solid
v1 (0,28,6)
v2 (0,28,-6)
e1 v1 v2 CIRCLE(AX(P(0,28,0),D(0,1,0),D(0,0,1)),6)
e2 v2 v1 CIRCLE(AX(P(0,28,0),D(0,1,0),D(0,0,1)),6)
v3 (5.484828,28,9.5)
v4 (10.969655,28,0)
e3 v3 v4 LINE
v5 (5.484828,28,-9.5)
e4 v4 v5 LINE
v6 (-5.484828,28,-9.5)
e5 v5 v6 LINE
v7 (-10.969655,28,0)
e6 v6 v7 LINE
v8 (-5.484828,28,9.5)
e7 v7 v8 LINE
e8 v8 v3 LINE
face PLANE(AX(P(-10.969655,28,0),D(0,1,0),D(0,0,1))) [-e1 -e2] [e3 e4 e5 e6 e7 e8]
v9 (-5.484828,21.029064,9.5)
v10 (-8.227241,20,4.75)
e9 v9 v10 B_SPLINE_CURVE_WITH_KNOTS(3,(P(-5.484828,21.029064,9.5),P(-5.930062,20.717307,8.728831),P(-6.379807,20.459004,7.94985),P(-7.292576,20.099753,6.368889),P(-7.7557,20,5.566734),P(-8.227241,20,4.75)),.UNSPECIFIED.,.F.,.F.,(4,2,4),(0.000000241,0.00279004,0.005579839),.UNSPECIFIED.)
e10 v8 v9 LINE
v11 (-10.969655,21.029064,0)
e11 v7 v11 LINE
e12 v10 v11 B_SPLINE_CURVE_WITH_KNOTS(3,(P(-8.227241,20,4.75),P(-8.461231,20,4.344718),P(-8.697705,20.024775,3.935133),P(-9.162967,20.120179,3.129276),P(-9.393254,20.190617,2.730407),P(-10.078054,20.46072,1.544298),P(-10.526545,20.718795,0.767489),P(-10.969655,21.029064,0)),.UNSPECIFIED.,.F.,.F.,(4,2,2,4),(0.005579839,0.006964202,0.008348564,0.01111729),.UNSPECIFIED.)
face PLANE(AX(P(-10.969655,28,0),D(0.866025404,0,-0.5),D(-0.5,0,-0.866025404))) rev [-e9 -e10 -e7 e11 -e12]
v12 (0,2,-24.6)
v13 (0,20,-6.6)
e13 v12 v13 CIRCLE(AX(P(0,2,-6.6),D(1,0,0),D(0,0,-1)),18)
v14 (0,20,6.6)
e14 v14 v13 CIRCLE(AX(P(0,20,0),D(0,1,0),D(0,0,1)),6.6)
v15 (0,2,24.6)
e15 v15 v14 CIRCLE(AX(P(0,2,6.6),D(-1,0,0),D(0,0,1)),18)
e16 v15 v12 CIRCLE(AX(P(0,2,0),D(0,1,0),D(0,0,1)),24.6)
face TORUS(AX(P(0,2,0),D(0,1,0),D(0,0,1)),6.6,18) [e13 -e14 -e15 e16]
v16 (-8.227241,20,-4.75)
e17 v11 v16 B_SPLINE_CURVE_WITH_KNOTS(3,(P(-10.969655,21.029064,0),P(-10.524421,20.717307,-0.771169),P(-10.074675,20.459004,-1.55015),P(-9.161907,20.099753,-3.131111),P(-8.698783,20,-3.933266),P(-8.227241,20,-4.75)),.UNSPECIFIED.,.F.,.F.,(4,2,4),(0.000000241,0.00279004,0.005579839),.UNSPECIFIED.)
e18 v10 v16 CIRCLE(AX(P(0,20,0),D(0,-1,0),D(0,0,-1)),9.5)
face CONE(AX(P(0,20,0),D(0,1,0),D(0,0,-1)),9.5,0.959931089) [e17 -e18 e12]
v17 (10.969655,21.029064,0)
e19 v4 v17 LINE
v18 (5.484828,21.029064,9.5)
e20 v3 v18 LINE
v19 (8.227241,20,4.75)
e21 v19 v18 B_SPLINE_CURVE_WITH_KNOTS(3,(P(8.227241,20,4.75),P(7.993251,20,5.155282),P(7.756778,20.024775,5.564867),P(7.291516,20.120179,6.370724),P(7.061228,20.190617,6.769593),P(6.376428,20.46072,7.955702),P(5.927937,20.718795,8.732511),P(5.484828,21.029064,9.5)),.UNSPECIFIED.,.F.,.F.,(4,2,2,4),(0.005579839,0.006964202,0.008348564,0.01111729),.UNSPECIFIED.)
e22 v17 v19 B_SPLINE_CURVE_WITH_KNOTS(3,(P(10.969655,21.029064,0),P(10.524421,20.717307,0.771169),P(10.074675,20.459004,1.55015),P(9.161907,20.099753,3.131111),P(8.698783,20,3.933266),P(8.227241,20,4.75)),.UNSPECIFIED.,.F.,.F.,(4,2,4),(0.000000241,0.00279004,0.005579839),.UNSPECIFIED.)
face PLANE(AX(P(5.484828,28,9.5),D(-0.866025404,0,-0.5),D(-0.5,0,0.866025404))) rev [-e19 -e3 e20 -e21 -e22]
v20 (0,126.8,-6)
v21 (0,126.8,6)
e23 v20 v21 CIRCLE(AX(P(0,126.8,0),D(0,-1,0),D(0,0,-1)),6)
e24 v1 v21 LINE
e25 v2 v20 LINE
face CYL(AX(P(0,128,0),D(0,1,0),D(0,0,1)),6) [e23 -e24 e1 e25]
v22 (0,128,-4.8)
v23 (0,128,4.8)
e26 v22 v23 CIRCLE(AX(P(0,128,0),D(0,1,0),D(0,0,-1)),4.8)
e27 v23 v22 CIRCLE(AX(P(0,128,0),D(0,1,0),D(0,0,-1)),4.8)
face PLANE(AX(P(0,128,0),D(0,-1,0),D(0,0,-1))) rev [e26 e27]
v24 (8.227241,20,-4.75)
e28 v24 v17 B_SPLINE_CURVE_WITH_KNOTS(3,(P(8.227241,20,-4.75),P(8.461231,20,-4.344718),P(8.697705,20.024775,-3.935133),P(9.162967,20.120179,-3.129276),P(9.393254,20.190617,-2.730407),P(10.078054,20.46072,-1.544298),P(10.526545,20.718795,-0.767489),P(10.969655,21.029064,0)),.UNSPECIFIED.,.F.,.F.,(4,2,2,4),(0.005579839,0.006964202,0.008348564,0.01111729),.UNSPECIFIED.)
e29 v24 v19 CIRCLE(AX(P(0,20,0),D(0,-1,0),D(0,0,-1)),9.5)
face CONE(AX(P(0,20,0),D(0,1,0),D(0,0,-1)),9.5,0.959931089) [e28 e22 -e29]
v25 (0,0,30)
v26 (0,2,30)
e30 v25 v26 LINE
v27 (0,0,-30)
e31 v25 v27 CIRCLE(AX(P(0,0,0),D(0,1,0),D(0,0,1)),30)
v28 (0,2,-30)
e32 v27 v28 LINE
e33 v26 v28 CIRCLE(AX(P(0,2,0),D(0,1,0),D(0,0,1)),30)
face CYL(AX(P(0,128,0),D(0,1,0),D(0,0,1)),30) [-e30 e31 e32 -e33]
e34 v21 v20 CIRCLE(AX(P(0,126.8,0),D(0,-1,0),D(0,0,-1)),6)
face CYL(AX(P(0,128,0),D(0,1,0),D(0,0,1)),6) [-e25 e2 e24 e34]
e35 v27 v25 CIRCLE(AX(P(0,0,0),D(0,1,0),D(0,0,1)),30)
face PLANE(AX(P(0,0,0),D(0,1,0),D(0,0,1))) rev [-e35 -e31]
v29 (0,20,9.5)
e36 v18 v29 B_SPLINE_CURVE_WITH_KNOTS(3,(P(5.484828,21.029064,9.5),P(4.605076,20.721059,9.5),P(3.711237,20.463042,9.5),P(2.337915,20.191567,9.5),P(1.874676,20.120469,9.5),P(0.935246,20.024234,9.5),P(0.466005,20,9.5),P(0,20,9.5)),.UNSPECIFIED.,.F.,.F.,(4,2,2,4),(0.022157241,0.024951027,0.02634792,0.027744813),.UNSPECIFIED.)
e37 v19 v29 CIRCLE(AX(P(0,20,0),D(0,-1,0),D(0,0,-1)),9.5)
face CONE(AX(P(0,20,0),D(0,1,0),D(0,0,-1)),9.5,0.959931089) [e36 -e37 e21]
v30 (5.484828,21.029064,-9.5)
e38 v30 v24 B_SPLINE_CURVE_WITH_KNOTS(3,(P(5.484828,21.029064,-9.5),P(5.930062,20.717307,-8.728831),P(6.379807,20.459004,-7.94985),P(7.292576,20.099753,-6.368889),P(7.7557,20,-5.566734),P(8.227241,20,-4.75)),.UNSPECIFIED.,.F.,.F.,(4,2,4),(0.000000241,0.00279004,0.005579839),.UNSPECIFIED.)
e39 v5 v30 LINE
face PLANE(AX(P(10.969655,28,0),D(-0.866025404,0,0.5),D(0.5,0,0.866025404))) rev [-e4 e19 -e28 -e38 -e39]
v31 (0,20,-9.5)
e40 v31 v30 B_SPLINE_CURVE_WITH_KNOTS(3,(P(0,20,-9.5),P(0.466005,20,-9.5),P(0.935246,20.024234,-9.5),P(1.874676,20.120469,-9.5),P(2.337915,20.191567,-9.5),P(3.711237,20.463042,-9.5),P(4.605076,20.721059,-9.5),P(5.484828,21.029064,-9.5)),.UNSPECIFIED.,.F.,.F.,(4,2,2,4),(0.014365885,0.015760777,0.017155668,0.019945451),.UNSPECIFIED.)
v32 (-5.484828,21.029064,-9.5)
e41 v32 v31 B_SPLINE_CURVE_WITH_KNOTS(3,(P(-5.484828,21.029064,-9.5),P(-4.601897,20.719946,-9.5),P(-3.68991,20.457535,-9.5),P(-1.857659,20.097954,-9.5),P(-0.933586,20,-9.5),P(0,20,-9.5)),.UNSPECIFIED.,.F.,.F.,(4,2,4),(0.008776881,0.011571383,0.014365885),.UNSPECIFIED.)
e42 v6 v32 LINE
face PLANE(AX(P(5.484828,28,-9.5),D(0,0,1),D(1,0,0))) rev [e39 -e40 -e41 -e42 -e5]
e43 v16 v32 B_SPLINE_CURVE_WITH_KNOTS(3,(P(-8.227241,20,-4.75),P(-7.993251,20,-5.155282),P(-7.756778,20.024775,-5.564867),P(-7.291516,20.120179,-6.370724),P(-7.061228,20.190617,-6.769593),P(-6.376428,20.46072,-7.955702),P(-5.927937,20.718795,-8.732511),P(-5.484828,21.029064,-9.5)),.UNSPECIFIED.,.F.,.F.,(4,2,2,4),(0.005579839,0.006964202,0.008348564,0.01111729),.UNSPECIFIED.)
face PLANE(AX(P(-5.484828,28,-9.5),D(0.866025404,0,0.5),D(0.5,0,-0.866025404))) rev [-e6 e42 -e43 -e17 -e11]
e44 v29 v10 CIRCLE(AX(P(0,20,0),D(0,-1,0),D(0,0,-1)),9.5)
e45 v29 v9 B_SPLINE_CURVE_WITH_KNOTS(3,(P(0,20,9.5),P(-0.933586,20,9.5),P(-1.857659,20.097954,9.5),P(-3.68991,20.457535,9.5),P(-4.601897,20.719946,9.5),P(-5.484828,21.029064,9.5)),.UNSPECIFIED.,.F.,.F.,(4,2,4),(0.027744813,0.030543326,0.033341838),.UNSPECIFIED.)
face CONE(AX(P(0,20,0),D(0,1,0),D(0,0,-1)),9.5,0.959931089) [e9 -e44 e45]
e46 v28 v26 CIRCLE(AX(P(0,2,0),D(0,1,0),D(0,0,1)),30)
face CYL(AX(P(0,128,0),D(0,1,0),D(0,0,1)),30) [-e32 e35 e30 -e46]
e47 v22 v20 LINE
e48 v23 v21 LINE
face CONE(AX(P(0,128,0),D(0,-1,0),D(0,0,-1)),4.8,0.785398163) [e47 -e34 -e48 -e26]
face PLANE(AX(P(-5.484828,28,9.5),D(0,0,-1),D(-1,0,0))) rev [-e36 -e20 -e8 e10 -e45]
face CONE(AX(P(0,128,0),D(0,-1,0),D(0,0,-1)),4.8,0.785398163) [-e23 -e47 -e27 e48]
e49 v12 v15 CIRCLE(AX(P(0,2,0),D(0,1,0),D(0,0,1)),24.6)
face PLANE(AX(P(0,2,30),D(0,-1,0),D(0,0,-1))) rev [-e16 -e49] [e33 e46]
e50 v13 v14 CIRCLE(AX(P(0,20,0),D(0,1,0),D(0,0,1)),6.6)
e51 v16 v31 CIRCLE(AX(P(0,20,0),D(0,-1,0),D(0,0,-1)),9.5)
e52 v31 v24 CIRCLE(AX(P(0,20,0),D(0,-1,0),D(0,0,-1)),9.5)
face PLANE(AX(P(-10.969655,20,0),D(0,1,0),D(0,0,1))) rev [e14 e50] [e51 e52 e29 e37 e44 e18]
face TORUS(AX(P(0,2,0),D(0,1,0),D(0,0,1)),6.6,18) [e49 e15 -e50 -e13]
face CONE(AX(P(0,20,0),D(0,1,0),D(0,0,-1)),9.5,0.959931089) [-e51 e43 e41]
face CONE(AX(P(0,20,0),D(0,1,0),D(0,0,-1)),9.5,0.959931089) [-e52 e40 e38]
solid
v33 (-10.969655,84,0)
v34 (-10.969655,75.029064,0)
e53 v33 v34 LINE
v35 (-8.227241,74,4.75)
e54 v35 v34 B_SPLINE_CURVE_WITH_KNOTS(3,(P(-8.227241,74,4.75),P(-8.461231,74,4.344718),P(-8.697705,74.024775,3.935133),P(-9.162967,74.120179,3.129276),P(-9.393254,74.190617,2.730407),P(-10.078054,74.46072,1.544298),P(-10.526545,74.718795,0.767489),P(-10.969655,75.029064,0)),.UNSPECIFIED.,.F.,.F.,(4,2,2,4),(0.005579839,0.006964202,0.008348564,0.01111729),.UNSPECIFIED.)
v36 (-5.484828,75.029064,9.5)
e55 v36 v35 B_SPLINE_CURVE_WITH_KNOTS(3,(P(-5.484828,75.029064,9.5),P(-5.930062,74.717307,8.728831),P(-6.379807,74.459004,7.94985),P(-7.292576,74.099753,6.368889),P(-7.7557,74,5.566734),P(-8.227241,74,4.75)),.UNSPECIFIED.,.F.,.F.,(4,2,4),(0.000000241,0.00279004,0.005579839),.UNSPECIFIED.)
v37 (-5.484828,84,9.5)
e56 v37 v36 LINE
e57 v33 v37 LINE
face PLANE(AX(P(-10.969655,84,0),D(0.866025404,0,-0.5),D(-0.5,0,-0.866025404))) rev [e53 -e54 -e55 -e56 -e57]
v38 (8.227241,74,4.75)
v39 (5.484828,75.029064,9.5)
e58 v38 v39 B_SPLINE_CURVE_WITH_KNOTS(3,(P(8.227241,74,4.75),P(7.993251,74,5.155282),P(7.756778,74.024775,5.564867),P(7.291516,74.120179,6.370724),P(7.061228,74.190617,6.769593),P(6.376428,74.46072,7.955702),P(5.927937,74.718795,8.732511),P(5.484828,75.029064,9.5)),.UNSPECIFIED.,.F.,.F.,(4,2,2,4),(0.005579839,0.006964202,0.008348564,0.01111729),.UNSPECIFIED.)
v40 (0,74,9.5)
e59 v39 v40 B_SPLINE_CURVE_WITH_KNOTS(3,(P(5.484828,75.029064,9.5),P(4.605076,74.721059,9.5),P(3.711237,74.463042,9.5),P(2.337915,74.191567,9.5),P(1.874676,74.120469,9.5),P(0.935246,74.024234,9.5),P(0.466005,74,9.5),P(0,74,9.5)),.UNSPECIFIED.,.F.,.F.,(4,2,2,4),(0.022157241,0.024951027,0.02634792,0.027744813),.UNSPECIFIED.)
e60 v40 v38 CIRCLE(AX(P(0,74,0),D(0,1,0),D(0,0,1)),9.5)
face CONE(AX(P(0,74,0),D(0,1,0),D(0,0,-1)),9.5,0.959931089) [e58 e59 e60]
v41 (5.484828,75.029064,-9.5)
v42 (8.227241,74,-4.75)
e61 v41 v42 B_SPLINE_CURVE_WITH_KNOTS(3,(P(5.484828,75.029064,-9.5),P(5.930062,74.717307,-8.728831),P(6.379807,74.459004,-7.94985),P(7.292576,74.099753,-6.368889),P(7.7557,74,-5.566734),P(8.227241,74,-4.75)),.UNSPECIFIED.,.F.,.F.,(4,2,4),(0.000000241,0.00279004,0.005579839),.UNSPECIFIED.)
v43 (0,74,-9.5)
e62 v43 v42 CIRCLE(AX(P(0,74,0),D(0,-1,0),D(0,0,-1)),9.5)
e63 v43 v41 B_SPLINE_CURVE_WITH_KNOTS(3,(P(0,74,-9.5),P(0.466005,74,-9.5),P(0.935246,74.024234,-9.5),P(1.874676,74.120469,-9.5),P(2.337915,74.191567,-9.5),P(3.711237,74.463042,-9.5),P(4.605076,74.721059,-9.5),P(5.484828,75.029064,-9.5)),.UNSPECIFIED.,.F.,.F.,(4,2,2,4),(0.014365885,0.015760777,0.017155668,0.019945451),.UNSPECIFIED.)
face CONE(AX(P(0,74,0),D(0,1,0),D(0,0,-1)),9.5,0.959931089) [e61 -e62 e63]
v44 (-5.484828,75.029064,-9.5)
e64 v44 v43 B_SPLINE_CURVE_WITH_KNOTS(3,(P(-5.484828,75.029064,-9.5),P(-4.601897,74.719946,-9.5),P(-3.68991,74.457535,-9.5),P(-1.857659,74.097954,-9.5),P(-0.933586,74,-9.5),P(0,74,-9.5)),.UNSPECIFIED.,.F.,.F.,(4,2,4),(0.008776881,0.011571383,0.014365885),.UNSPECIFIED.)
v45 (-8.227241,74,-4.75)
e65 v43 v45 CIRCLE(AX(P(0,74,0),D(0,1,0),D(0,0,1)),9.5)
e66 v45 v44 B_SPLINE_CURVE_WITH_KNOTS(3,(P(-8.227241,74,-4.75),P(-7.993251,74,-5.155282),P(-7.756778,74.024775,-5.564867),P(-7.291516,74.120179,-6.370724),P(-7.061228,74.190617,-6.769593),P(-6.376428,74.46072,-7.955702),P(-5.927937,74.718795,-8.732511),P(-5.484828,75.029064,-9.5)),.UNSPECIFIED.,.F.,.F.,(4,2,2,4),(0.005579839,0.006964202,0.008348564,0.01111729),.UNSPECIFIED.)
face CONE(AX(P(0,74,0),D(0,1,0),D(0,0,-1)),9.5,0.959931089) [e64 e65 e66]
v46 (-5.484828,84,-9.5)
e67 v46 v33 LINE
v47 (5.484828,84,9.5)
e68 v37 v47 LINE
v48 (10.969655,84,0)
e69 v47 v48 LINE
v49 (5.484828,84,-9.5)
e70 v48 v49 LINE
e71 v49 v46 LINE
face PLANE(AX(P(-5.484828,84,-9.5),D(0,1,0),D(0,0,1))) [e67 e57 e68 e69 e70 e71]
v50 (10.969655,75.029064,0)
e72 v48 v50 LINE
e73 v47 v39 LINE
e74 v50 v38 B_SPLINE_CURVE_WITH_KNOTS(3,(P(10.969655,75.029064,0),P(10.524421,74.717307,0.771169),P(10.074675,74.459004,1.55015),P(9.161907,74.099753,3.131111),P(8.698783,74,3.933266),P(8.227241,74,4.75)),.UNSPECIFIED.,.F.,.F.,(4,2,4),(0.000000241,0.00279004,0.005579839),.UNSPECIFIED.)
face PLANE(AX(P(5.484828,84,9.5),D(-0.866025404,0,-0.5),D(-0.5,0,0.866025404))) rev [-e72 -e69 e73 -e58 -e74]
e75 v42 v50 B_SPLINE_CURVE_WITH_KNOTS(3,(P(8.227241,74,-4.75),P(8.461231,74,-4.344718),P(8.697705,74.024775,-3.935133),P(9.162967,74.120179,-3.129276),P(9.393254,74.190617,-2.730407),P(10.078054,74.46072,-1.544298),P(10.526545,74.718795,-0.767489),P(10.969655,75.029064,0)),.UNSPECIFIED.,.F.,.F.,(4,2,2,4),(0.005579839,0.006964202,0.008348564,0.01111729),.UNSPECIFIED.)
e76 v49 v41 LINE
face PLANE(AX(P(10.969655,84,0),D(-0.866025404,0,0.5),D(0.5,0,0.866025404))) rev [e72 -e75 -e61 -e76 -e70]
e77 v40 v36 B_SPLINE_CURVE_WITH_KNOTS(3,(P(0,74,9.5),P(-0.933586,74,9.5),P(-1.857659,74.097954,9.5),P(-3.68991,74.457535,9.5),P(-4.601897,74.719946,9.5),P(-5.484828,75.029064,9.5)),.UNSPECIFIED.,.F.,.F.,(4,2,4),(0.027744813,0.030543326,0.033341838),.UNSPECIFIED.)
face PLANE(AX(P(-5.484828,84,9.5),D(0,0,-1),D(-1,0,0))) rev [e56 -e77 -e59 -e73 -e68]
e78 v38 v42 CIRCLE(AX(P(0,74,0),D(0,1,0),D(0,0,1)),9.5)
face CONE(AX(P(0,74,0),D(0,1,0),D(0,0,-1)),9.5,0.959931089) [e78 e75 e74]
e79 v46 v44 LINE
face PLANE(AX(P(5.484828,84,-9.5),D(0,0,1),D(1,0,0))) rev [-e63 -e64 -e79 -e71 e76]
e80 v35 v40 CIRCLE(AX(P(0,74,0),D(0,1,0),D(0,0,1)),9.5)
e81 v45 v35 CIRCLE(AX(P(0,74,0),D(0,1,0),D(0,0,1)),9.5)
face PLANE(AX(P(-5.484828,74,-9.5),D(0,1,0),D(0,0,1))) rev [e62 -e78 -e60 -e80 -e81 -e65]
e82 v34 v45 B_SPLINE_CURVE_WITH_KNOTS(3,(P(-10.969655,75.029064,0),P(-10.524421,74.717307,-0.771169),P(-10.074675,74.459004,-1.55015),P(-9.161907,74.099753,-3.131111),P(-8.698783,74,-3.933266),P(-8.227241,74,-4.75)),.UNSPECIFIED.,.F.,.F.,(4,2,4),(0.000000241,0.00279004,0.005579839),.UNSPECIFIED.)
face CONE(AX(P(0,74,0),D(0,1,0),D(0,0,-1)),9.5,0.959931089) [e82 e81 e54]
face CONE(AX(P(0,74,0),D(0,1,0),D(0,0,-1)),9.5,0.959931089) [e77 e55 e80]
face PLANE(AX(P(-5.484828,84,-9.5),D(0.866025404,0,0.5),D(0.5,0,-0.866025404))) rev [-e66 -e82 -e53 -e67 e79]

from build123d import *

# Parameters (mm, degrees)
CHAMFER1_SIZE       = 1.2
BOSS_EXTRUDE1_START = 20
BOSS_EXTRUDE1_DEPTH = 8
BOSS_EXTRUDE2_START = 74
BOSS_EXTRUDE2_DEPTH = 10
SKETCH5_R           = 12.439310229
SKETCH5_R_2         = 9.5
CUT_EXTRUDE1_DEPTH  = 6.4
CUT_EXTRUDE1_TAPER  = 55
SKETCH6_R           = 12.439310229
SKETCH6_R_2         = 9.5
CUT_EXTRUDE4_DEPTH  = 5
CUT_EXTRUDE4_DRAFT  = -55


with BuildPart() as part:
    # Sketch2 → Revolve1 (revolve)
    with BuildSketch(Plane(origin=(0, 0, 0), x_dir=(0, 0, -1), z_dir=(1, 0, 0)), mode=Mode.PRIVATE) as revolve1_sk:
        with BuildLine():
            Line((0, 128), (6, 128))
            Line((6, 128), (6, 20))
            Line((6, 20), (6.6, 20))
            ThreePointArc((6.6, 20), (19.327922061, 14.727922061), (24.6, 2))
            Line((24.6, 2), (30, 2))
            Line((30, 2), (30, 0))
            Line((30, 0), (0, 0))
            Line((0, 0), (0, 128))
        make_face()
    revolve(revolve1_sk.sketch.rotate(Axis((0, 128, 0), (0, -1, 0)), 180), axis=Axis((0, 128, 0), (0, -1, 0)))

    # Chamfer1
    chamfer1_edges = [part.edges().sort_by_distance(p)[0] for p in [
        (0, 128, -6),
    ]]
    chamfer(chamfer1_edges, length=CHAMFER1_SIZE)

    # Sketch3 → Boss-Extrude1 (add)
    with BuildSketch(Plane(origin=(0, 0, 0), x_dir=(1, 0, 0), z_dir=(0, 1, 0)).offset(BOSS_EXTRUDE1_START)):
        Polygon((-10.969655115, 0), (-5.484827557, -9.5), (5.484827557, -9.5), (10.969655115, 0), (5.484827557, 9.5), (-5.484827557, 9.5), align=None)
    extrude(amount=BOSS_EXTRUDE1_DEPTH)

    # Sketch5 → Cut-Extrude1 (cut)
    with BuildSketch(Plane.XZ.offset(-20)):
        Circle(SKETCH5_R)
        Circle(SKETCH5_R_2, mode=Mode.SUBTRACT)
    extrude(amount=-CUT_EXTRUDE1_DEPTH, taper=CUT_EXTRUDE1_TAPER, mode=Mode.SUBTRACT)


with BuildPart() as body_2:
    # Sketch4 → Boss-Extrude2 (new body)
    with BuildSketch(Plane(origin=(0, 0, 0), x_dir=(1, 0, 0), z_dir=(0, 1, 0)).offset(BOSS_EXTRUDE2_START)):
        Polygon((-5.484827557, 9.5), (-10.969655115, 0), (-5.484827557, -9.5), (5.484827557, -9.5), (10.969655115, 0), (5.484827557, 9.5), align=None)
    extrude(amount=BOSS_EXTRUDE2_DEPTH)


with BuildPart() as cut_extrude4_tool:
    # Sketch6 → Cut-Extrude4 (with draft: the straight prism first)
    with BuildSketch(Plane.XZ.offset(-74)):
        Circle(SKETCH6_R)
        Circle(SKETCH6_R_2, mode=Mode.SUBTRACT)
    extrude(amount=-CUT_EXTRUDE4_DEPTH)
    # Cut-Extrude4: the draft: its side faces are tilted about the plane it starts from
    cut_extrude4_sides = [cut_extrude4_tool.faces().sort_by_distance(p)[0] for p in [
        (-12.439310229, 76.5, 0),
        (-9.5, 76.5, 0),
    ]]
    draft(cut_extrude4_sides, Plane.XZ.offset(-74), CUT_EXTRUDE4_DRAFT)


with BuildPart() as body_2_1:
    add(body_2.part)

    # Cut-Extrude4: cut by cut_extrude4_tool
    add(cut_extrude4_tool.part, mode=Mode.SUBTRACT)


solid = Compound([part.part, body_2_1.part])
